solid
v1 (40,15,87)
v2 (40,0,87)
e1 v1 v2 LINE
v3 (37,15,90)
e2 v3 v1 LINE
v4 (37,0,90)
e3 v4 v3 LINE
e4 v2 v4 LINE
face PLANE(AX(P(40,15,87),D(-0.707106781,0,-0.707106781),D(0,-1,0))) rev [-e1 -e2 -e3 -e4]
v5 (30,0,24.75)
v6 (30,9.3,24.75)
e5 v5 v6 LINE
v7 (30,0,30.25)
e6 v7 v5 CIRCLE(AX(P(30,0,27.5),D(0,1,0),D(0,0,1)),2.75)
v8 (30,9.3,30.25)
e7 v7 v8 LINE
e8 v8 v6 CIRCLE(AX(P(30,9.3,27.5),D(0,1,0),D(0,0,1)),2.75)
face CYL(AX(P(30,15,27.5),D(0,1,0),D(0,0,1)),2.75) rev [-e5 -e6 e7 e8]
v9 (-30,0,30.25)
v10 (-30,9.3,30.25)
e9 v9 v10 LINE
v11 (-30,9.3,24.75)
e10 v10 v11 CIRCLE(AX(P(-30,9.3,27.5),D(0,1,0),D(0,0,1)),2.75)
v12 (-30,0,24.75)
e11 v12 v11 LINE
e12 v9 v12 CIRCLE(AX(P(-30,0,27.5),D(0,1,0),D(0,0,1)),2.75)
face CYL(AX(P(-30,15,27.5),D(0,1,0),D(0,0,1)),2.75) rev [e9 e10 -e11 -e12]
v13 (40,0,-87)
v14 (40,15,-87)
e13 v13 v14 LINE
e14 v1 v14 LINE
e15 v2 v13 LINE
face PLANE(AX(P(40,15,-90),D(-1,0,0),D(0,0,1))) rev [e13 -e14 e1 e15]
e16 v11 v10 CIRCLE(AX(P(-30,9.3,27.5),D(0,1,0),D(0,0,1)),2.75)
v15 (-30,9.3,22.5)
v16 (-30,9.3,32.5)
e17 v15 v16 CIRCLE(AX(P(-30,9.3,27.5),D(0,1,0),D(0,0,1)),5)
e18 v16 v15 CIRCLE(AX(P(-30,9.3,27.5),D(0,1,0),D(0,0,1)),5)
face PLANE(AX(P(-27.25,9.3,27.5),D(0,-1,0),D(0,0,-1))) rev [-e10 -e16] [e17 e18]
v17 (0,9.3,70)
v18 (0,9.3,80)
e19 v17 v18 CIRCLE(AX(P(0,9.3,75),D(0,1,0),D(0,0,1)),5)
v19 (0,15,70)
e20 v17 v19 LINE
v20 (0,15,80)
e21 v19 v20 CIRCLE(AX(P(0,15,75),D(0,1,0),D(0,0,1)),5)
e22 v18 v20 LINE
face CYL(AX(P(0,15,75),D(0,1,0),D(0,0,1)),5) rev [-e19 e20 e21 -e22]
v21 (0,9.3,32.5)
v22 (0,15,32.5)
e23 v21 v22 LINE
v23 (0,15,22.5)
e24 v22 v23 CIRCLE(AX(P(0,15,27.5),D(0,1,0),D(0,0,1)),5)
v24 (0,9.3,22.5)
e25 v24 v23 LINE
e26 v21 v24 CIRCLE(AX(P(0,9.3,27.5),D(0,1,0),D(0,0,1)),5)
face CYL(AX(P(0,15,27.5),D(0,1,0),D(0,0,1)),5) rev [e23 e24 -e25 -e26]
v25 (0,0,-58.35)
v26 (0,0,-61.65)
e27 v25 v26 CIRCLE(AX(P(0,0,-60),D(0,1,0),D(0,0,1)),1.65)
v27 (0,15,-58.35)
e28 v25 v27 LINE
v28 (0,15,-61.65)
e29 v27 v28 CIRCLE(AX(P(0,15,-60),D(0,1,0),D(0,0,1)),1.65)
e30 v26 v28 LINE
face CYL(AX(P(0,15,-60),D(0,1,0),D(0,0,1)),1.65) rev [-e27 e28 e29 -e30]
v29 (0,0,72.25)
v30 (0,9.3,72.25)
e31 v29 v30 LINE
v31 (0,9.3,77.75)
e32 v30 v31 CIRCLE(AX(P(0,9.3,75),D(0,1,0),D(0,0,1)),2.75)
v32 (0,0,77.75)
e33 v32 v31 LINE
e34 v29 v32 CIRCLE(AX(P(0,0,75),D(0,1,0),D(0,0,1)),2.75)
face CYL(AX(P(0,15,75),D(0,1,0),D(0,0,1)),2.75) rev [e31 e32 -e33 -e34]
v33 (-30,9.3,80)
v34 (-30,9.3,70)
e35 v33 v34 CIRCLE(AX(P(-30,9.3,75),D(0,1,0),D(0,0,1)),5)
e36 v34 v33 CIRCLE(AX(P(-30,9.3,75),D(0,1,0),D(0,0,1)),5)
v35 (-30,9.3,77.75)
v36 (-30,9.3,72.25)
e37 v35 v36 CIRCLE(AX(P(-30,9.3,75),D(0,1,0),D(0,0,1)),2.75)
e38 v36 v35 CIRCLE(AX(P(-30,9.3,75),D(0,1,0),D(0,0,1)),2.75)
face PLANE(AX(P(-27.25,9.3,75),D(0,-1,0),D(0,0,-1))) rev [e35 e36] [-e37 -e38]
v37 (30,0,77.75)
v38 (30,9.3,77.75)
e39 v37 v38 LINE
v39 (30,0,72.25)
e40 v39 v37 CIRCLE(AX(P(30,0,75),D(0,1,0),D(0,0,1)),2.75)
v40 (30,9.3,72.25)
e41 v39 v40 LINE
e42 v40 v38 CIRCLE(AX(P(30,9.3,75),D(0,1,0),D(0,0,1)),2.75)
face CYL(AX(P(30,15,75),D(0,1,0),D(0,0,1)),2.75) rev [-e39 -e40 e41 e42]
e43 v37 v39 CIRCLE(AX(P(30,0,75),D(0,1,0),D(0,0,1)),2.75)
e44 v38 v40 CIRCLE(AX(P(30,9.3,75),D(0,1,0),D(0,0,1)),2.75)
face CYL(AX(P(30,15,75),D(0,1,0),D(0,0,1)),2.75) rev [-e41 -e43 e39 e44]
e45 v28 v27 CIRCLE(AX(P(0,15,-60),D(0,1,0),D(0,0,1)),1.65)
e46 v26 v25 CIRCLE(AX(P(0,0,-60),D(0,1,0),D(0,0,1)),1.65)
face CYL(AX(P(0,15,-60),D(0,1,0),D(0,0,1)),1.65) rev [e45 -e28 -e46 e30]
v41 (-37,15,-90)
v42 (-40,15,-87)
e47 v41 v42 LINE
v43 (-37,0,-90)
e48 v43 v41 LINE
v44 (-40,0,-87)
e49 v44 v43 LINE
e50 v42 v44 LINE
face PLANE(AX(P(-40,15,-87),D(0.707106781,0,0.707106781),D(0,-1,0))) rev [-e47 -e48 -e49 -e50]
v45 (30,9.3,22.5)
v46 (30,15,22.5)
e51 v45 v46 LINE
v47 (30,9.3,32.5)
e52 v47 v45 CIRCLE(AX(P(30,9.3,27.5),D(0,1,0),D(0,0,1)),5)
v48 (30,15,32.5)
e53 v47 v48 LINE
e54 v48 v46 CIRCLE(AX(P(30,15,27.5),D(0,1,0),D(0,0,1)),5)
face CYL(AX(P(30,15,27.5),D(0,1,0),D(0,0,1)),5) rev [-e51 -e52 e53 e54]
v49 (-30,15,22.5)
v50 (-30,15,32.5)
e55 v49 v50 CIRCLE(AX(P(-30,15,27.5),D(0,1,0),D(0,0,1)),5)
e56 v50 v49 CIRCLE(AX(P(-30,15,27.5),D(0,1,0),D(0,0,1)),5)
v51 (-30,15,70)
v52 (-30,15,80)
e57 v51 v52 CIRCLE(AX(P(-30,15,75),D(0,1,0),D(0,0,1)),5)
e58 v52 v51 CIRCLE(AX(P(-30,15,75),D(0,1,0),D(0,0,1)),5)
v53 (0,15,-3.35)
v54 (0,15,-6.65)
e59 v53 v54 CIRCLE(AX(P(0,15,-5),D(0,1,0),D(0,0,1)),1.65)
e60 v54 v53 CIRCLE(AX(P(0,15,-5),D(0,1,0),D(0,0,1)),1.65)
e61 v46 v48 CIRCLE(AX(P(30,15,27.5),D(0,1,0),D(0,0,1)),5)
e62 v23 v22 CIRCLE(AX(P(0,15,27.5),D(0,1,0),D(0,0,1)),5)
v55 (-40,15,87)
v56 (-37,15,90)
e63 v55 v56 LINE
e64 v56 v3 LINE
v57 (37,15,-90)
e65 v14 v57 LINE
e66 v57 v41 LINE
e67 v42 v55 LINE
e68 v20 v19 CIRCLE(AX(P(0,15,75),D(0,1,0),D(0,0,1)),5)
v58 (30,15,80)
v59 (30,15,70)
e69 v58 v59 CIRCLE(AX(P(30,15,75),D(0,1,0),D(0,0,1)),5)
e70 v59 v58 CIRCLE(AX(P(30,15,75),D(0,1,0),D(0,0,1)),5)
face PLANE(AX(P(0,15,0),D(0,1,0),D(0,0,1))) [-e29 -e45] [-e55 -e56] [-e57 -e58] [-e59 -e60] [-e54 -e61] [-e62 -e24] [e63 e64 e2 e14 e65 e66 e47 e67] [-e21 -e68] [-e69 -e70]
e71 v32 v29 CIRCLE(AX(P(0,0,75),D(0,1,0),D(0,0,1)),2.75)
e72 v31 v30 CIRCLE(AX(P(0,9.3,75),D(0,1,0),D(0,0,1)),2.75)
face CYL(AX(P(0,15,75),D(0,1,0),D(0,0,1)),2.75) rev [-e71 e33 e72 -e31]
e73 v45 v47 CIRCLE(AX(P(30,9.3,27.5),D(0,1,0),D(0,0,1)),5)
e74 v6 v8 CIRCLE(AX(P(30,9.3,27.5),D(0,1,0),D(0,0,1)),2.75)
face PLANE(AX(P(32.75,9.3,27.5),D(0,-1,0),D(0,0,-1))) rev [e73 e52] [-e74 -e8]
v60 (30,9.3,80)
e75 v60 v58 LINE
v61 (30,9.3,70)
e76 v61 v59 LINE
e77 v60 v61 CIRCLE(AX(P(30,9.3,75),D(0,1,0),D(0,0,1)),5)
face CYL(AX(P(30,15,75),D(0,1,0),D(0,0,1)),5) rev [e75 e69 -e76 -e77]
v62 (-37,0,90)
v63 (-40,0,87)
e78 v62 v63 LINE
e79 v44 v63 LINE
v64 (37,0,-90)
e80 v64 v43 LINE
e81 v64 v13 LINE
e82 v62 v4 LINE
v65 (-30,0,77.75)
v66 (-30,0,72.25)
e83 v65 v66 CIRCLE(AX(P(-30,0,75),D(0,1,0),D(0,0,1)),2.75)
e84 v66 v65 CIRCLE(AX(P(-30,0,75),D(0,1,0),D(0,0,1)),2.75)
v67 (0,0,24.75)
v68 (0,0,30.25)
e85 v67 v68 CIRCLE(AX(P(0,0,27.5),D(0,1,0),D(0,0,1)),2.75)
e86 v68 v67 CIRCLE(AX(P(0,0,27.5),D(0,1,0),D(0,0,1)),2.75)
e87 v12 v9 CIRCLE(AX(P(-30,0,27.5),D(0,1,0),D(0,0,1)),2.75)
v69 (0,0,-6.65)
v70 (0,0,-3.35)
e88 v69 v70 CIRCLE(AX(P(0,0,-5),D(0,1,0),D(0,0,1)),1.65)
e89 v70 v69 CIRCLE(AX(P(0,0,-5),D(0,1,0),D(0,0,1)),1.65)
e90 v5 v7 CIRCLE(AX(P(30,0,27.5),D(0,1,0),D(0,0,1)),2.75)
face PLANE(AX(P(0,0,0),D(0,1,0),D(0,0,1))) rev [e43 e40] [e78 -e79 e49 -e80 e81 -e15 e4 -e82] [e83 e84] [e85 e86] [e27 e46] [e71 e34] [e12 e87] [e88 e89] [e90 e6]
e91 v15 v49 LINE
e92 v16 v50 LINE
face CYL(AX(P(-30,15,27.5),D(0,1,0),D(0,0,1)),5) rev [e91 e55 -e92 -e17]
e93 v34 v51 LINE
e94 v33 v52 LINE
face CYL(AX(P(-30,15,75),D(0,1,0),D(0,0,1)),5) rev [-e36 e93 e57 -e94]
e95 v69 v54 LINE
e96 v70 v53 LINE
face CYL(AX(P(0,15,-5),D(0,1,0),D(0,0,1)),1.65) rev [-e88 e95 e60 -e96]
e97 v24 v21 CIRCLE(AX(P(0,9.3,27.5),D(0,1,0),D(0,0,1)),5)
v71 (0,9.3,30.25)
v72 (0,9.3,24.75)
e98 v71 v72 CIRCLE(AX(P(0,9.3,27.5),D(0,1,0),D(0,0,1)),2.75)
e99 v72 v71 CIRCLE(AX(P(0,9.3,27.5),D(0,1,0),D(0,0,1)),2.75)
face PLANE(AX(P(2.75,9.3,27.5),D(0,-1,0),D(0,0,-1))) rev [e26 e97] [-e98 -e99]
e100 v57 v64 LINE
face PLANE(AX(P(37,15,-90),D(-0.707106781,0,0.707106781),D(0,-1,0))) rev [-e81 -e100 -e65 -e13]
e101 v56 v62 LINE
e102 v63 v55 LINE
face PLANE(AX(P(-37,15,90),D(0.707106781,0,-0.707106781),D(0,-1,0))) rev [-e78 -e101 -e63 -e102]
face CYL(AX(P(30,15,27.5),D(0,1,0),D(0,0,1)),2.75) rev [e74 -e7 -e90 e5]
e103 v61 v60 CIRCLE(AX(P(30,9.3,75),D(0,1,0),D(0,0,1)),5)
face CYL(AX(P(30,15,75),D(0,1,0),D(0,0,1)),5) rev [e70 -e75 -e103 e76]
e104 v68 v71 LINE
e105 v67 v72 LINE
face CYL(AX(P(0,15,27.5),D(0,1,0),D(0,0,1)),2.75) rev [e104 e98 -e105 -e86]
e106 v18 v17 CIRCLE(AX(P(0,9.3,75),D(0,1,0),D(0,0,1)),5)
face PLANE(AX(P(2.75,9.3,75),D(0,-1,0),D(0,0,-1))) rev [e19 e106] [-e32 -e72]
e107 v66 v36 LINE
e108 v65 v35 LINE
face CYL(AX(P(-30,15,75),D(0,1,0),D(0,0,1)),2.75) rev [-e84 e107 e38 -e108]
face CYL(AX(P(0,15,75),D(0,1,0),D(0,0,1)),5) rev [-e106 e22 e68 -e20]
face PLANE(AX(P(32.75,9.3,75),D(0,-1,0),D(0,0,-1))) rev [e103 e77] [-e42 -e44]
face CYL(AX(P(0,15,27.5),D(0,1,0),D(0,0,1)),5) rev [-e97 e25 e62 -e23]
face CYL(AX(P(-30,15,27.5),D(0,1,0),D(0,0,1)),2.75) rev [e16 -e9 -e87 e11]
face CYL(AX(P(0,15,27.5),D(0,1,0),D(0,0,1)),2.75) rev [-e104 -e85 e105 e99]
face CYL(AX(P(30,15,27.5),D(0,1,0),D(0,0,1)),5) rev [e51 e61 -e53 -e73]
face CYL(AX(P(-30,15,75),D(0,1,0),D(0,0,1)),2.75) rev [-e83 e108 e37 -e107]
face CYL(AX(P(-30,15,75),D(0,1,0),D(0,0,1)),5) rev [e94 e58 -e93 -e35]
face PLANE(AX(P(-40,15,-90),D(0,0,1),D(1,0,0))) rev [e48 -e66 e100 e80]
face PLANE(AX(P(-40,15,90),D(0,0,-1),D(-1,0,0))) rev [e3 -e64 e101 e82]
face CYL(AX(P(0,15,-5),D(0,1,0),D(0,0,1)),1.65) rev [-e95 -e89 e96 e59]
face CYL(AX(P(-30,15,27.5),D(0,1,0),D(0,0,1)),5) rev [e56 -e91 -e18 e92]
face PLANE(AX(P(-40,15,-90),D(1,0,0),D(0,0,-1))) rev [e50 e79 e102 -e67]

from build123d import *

# Parameters (mm, degrees)
SKETCH_1_W                = 80
SKETCH_1_H                = 180
EXTRUDE_1_DEPTH           = 15
CHAMFER_1_SIZE            = 3
HOLE_WIZARD_M4_1_D        = 3.3
HOLE_WIZARD_M4_1_DEPTH    = 20
HOLE_WIZARD_M4_1_TIP      = 0.991420021
HOLE_WIZARD_1_D           = 5.5
HOLE_WIZARD_1_DEPTH       = 20
HOLE_WIZARD_1_CBORE_D     = 10
HOLE_WIZARD_1_CBORE_DEPTH = 5.7
HOLE_WIZARD_1_TIP         = 1.652366702
HOLE_WIZARD_2_D           = 5.5
HOLE_WIZARD_2_DEPTH       = 15
HOLE_WIZARD_2_CBORE_D     = 10
HOLE_WIZARD_2_CBORE_DEPTH = 5.7
HOLE_WIZARD_2_TIP         = 1.652366702


with BuildPart() as part:
    # 草图1 → 凸台-拉伸1 (new body)
    with BuildSketch(Plane(origin=(0, 0, 0), x_dir=(1, 0, 0), z_dir=(0, 1, 0))):
        Rectangle(SKETCH_1_W, SKETCH_1_H)
    extrude(amount=EXTRUDE_1_DEPTH)

    # 倒角1
    chamfer_1_edges = [part.edges().sort_by_distance(p)[0] for p in [
        (40, 7.5, 90),
        (-40, 7.5, 90),
        (-40, 7.5, -90),
        (40, 7.5, -90),
    ]]
    chamfer(chamfer_1_edges, length=CHAMFER_1_SIZE)

    # M4 螺纹孔1
    with Locations(Plane(origin=(0, 15, 0), x_dir=(1, 0, 0), z_dir=(0, 1, 0))):
        with Locations((0, 60), (0, 5)):
            Hole(HOLE_WIZARD_M4_1_D / 2, depth=HOLE_WIZARD_M4_1_DEPTH)
            with Locations((0, 0, -(HOLE_WIZARD_M4_1_DEPTH + HOLE_WIZARD_M4_1_TIP / 2))):  # 118° drill point
                Cone(0, HOLE_WIZARD_M4_1_D / 2, HOLE_WIZARD_M4_1_TIP, mode=Mode.SUBTRACT)

    # 打孔尺寸(%根据)内六角圆柱头螺钉的类型1
    with Locations(Plane(origin=(0, 15, 0), x_dir=(1, 0, 0), z_dir=(0, 1, 0))):
        with Locations((-30, -27.5), (0, -27.5), (30, -27.5)):
            CounterBoreHole(HOLE_WIZARD_1_D / 2, HOLE_WIZARD_1_CBORE_D / 2, HOLE_WIZARD_1_CBORE_DEPTH, depth=HOLE_WIZARD_1_DEPTH)
            with Locations((0, 0, -(HOLE_WIZARD_1_DEPTH + HOLE_WIZARD_1_TIP / 2))):  # 118° drill point
                Cone(0, HOLE_WIZARD_1_D / 2, HOLE_WIZARD_1_TIP, mode=Mode.SUBTRACT)

    # 打孔尺寸(%根据)内六角圆柱头螺钉的类型2
    with Locations(Plane(origin=(0, 15, 0), x_dir=(1, 0, 0), z_dir=(0, 1, 0))):
        with Locations((-30, -75), (0, -75), (30, -75)):
            CounterBoreHole(HOLE_WIZARD_2_D / 2, HOLE_WIZARD_2_CBORE_D / 2, HOLE_WIZARD_2_CBORE_DEPTH, depth=HOLE_WIZARD_2_DEPTH)
            with Locations((0, 0, -(HOLE_WIZARD_2_DEPTH + HOLE_WIZARD_2_TIP / 2))):  # 118° drill point
                Cone(0, HOLE_WIZARD_2_D / 2, HOLE_WIZARD_2_TIP, mode=Mode.SUBTRACT)


solid = part.part
